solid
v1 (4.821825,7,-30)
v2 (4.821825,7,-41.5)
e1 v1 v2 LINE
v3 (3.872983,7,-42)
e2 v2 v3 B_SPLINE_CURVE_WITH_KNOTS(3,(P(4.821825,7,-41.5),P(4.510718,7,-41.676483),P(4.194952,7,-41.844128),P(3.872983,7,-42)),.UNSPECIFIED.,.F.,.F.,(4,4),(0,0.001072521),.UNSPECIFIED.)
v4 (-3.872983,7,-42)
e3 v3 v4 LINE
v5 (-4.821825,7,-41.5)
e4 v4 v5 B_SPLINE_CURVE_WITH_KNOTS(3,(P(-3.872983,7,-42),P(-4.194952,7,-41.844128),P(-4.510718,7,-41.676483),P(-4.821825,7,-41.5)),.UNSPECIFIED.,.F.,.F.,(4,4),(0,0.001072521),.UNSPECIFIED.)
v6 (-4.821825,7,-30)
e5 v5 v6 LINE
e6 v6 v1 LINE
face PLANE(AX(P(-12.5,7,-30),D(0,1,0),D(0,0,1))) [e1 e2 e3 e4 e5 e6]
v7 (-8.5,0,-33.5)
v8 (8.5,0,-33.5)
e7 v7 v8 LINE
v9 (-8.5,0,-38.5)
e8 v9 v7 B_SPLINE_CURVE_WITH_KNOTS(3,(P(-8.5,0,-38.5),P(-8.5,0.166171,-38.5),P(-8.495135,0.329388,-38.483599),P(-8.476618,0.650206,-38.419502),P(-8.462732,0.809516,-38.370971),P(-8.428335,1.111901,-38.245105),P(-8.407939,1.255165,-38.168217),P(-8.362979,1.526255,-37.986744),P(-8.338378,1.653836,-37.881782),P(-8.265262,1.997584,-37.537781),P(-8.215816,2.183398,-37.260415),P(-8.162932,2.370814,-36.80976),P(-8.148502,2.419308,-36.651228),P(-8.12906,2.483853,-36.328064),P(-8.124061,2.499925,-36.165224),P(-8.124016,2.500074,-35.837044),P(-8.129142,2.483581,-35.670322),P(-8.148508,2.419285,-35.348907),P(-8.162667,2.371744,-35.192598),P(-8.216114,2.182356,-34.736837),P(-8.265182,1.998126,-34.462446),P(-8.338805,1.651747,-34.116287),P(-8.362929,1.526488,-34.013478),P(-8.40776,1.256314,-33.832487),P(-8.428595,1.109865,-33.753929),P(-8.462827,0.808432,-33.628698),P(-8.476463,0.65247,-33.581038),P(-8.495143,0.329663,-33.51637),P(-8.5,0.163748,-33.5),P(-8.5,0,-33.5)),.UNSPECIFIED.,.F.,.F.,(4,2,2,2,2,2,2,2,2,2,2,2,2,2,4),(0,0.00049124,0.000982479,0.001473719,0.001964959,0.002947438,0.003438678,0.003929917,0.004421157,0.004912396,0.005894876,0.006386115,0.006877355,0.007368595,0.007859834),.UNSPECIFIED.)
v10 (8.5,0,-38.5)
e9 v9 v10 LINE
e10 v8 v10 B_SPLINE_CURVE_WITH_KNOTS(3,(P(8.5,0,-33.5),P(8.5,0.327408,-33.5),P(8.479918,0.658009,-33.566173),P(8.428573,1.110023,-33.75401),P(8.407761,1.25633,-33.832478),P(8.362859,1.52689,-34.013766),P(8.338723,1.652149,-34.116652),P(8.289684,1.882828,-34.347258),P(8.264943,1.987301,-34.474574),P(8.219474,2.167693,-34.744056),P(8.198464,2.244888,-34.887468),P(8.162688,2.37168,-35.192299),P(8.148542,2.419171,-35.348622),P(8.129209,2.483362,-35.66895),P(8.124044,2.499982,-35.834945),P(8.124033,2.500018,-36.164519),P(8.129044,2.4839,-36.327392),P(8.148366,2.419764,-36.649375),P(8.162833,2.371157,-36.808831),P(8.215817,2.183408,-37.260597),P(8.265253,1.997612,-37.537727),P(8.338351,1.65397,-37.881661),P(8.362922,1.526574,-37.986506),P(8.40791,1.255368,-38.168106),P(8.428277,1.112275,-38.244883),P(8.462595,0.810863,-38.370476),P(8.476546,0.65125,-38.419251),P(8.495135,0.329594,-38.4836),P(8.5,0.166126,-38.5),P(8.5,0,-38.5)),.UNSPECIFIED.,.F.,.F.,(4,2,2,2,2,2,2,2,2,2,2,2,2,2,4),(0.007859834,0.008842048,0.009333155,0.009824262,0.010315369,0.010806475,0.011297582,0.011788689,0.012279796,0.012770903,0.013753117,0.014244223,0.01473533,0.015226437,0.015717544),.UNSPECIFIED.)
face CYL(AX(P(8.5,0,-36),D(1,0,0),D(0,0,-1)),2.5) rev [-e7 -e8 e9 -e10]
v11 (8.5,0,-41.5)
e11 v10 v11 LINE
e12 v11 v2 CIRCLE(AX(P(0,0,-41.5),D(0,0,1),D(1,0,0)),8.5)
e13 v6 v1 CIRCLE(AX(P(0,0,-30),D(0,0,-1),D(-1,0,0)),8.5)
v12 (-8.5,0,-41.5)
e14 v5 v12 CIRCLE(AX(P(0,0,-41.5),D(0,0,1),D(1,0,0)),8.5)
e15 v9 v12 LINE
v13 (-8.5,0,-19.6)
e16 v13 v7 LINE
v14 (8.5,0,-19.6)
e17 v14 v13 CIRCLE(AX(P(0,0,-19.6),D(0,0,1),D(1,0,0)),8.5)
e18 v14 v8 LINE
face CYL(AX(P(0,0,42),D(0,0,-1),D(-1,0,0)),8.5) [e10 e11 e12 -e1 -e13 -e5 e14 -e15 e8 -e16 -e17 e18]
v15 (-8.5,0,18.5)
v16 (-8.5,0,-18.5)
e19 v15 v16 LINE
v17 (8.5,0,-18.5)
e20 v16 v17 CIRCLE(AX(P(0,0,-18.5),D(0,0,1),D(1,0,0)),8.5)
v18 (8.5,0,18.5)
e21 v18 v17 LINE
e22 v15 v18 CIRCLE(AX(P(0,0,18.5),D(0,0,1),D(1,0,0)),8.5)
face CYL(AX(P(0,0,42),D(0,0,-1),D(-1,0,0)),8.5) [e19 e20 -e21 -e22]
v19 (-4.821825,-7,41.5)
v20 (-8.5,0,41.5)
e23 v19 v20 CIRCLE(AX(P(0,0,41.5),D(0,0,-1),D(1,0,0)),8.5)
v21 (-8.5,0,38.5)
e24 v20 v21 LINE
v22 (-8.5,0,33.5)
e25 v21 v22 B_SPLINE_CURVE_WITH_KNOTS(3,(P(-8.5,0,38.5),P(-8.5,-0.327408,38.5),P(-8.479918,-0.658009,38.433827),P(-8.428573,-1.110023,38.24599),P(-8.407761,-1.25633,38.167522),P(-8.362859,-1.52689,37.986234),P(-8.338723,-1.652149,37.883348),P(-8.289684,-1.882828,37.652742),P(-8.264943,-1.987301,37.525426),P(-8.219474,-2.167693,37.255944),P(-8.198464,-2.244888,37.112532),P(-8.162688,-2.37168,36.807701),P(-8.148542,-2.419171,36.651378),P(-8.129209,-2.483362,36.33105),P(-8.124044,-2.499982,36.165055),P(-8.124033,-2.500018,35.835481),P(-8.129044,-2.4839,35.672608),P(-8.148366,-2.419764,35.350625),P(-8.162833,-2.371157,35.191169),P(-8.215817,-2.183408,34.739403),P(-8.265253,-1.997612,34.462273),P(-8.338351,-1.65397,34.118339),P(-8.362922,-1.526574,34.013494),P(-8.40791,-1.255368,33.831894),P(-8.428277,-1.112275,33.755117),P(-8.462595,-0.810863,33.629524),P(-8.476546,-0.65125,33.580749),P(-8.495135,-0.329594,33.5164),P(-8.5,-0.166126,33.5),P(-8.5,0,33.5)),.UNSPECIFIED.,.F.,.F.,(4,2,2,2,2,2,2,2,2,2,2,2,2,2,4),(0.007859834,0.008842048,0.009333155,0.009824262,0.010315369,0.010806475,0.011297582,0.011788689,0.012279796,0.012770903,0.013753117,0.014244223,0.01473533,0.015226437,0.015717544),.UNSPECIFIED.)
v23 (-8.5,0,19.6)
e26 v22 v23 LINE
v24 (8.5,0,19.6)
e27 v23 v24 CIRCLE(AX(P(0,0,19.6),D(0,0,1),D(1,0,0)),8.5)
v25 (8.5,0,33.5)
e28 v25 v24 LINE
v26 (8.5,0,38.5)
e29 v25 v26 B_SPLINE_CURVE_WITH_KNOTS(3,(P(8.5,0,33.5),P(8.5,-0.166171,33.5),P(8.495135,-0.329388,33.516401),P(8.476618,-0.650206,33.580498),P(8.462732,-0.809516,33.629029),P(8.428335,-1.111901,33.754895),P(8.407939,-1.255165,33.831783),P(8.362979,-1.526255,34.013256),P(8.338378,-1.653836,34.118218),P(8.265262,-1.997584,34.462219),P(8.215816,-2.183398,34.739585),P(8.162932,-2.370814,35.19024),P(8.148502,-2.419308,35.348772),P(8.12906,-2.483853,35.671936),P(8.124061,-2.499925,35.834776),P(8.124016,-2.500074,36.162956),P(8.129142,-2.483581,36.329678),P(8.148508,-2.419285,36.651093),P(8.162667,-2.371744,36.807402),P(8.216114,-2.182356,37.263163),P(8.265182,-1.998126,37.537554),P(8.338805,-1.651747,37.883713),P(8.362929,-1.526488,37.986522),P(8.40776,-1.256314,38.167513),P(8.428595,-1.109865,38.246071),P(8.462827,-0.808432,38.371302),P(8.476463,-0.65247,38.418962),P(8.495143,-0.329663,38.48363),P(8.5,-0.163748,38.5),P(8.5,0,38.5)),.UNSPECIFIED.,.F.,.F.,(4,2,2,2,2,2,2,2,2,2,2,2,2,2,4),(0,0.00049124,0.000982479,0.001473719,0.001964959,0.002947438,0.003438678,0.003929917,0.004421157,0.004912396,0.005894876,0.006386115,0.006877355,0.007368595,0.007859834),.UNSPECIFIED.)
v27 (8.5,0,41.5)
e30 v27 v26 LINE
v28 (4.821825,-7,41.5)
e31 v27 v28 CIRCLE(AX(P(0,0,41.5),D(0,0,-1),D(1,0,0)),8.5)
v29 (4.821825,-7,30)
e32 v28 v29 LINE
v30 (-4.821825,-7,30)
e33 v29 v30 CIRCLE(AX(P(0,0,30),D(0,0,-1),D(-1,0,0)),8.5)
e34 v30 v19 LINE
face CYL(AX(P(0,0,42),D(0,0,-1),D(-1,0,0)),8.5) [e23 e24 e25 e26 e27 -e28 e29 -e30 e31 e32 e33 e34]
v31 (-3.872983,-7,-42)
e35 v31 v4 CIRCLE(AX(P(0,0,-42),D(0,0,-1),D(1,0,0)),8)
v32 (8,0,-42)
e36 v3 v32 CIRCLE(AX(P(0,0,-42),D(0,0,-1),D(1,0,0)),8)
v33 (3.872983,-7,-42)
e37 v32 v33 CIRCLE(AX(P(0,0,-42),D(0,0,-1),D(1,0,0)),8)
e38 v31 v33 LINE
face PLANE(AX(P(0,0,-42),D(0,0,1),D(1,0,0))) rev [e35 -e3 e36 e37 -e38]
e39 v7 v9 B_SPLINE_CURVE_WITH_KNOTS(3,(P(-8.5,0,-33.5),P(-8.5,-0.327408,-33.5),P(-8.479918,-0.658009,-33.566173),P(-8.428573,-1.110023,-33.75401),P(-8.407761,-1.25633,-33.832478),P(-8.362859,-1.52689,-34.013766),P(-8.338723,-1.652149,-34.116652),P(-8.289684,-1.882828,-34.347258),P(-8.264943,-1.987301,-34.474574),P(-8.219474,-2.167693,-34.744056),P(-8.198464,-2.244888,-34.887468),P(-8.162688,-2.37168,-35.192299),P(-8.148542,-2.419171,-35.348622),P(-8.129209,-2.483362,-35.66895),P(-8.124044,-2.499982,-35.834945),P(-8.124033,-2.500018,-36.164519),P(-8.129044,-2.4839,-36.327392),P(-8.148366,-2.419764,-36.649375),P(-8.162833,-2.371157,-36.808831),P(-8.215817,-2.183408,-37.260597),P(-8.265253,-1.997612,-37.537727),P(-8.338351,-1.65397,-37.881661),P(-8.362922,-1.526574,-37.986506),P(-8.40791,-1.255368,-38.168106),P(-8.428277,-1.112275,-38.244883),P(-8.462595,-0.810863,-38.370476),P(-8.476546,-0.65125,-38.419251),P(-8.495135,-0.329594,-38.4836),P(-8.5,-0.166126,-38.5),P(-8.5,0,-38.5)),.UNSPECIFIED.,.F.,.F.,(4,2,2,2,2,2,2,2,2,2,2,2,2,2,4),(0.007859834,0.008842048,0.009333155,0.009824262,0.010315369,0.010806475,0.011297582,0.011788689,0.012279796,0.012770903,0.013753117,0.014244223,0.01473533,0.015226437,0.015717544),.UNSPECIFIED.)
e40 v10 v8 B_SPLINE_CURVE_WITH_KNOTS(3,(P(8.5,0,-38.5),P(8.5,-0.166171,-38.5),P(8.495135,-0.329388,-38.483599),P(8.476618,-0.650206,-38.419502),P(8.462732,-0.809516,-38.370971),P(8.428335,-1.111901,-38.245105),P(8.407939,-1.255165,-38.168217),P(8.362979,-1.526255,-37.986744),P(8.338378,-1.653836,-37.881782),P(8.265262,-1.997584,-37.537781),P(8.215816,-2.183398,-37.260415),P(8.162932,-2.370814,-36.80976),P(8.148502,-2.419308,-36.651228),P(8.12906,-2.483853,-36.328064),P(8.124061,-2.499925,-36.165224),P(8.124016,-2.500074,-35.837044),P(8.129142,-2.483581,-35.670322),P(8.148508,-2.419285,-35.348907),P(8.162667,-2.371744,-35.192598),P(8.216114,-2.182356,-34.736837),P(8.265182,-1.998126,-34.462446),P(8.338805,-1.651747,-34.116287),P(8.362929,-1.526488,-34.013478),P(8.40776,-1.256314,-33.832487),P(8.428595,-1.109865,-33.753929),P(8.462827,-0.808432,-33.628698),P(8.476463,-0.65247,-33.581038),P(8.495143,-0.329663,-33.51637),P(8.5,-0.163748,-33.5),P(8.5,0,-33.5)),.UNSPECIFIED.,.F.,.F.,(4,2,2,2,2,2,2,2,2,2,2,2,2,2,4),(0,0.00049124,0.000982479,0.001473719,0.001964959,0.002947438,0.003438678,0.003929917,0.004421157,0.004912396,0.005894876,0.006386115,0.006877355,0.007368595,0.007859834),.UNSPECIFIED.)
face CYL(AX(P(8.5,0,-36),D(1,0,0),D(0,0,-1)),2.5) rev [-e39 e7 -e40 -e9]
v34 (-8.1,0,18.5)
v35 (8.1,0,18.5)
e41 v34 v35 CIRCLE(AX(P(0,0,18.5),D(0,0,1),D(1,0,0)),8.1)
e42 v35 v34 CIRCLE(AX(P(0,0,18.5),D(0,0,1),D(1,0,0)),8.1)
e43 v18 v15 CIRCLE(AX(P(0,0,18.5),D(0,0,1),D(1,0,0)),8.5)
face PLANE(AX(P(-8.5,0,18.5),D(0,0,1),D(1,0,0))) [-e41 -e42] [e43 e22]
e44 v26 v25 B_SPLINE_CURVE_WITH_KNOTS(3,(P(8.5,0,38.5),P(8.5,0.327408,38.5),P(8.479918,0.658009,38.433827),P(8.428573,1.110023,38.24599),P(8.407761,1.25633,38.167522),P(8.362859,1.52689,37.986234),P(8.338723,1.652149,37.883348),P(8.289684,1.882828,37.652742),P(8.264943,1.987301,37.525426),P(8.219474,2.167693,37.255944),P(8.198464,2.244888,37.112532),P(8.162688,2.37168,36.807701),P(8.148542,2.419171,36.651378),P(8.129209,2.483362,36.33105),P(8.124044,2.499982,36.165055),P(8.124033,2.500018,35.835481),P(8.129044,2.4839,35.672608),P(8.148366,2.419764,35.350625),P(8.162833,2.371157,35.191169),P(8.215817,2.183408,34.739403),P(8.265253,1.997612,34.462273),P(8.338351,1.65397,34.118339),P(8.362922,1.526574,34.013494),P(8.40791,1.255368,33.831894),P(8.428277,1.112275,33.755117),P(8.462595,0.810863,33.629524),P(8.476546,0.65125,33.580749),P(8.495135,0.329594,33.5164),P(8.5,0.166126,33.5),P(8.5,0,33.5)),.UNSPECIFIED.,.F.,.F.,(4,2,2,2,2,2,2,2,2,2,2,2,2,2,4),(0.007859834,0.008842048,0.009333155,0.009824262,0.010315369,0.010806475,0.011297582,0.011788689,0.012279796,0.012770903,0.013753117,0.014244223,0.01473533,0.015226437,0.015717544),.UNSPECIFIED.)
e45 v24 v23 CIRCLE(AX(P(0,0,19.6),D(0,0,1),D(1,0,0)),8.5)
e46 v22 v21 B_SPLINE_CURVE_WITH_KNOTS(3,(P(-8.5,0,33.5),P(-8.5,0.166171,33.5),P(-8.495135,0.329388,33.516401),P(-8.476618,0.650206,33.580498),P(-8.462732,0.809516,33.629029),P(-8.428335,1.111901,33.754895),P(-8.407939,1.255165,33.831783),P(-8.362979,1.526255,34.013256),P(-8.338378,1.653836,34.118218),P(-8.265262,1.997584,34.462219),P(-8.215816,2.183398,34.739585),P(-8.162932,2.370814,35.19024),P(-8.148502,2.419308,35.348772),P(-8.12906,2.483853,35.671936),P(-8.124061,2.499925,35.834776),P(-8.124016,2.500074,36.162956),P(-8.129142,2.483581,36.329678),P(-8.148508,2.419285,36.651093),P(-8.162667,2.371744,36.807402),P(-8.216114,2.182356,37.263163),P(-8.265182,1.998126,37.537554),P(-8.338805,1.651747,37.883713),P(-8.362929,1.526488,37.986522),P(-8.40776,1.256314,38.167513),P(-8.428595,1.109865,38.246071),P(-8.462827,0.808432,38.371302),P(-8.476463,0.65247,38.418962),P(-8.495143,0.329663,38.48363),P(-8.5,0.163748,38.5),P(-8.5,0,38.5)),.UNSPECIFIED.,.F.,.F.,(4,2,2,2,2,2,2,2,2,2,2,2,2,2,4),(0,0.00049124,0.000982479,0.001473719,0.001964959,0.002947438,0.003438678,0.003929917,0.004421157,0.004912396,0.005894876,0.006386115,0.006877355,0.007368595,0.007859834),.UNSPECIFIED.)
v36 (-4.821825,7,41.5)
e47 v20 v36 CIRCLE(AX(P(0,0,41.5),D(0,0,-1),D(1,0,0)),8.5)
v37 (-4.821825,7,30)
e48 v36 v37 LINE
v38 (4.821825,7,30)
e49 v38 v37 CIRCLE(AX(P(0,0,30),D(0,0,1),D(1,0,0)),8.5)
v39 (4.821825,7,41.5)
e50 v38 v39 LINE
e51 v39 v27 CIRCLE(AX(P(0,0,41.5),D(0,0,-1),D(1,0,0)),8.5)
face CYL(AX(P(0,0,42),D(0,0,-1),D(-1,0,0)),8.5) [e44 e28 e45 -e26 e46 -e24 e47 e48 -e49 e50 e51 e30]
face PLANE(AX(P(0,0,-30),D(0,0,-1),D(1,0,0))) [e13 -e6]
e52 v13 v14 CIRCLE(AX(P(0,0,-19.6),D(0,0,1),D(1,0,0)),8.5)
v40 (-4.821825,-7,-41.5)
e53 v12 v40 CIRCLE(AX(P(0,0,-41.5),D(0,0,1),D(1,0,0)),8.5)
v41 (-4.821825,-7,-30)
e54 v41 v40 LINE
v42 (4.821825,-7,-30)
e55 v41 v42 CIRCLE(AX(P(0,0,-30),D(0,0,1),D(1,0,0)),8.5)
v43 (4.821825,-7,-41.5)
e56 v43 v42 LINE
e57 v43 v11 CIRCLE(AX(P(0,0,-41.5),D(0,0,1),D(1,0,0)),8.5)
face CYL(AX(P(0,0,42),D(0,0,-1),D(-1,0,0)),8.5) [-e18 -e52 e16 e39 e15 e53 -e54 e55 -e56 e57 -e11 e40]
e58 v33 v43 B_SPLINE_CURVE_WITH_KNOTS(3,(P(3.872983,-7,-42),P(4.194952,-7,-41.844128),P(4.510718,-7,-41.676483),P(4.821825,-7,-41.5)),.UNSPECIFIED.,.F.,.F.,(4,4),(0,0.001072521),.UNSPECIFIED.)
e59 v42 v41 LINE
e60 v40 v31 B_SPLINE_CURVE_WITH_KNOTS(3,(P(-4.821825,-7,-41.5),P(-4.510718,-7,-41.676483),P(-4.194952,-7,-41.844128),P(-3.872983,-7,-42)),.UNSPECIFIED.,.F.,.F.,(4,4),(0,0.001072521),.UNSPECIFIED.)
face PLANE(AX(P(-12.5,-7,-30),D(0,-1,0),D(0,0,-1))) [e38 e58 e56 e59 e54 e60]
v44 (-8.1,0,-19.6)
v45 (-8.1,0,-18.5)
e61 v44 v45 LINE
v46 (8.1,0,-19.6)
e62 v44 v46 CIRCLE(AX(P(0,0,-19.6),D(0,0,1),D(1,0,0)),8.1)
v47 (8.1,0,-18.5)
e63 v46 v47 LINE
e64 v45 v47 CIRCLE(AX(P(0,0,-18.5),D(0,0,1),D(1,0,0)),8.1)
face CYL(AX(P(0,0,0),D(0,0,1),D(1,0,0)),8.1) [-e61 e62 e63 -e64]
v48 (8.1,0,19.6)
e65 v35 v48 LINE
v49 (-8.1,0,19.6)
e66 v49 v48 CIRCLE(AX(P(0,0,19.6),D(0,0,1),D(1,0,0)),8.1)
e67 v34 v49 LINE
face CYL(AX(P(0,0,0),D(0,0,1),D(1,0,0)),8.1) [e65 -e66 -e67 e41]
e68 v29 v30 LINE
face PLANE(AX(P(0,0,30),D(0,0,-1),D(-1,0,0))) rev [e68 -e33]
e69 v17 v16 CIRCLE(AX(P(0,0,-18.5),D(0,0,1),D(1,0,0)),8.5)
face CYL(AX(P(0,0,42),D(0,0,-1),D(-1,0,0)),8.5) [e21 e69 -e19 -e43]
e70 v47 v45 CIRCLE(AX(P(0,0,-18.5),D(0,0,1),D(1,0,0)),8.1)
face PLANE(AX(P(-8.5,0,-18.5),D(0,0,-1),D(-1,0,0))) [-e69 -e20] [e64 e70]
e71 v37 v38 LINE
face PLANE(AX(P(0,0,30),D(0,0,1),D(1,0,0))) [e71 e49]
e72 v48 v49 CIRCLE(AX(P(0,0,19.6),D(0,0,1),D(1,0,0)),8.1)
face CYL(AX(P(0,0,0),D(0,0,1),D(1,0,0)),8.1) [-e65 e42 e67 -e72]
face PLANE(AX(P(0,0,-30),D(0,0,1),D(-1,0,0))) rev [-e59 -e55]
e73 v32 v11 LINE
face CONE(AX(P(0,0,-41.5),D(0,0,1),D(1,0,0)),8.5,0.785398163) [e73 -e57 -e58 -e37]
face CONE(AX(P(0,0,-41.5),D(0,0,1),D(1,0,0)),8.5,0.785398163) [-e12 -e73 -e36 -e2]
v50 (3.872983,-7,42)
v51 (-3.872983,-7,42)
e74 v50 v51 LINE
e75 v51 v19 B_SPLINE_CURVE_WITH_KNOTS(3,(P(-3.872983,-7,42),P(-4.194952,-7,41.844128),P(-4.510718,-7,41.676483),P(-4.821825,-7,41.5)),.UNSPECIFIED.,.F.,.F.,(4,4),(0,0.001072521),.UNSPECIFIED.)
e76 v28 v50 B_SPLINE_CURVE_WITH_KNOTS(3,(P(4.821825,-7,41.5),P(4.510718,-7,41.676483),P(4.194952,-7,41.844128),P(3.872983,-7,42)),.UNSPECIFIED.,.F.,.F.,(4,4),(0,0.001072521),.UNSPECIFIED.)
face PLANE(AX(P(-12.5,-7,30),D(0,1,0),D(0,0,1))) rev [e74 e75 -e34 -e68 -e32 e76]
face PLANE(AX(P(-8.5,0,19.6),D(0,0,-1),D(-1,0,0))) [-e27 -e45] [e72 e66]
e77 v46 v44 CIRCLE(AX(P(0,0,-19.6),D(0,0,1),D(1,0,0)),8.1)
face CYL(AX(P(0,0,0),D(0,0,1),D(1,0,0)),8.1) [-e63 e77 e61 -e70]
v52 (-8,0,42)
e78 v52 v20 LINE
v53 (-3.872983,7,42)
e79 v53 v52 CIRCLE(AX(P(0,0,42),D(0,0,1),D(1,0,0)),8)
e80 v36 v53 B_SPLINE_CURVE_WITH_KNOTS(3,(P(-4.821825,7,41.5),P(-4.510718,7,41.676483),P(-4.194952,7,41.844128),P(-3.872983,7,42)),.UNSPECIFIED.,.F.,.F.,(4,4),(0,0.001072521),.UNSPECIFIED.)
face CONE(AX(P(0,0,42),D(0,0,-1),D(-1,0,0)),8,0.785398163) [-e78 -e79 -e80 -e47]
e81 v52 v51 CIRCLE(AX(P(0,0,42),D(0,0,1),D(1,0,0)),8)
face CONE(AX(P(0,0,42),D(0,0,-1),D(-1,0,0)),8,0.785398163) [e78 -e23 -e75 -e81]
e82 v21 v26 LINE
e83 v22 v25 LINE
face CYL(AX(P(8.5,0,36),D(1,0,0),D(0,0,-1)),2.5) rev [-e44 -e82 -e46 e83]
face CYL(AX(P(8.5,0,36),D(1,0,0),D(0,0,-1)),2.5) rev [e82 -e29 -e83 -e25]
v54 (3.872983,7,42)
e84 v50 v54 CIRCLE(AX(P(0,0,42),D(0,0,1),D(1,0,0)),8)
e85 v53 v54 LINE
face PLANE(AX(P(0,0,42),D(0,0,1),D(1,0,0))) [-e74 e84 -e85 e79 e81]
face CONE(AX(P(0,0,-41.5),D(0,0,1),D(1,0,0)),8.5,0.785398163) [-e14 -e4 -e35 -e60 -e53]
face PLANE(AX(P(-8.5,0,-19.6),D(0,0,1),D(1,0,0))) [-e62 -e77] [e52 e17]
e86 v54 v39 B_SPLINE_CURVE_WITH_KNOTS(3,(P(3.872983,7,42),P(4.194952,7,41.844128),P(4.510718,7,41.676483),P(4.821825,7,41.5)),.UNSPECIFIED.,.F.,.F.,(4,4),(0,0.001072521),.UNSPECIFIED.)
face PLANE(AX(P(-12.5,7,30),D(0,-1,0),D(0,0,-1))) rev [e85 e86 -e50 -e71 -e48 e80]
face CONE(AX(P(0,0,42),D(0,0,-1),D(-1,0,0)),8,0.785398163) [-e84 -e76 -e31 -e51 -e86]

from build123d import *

# Parameters (mm, degrees)
SKETCH_1_R          = 8.5
EXTRUDE_1_DEPTH     = 42
SKETCH_2_W          = 25
SKETCH_2_H          = 3
CUT_EXTRUDE_1_DEPTH = 12
CHAMFER_2_SIZE      = 0.5
HOLE_WIZARD_M6_1_D  = 5
SKETCH_5_W          = 0.4
SKETCH_5_H          = 1.1


with BuildPart() as part:
    # 草图1 → 凸台-拉伸1 (new, symmetric)
    with BuildSketch(Plane.XY):
        with Locations(Location((0, 0, 0), (0, 0, 180))):
            Circle(SKETCH_1_R)
    extrude(amount=EXTRUDE_1_DEPTH, both=True)

    # 草图2 → 切除-拉伸1 (cut)
    with BuildSketch(Plane.XY.offset(42)):
        with Locations((0, 8.5)):
            Rectangle(SKETCH_2_W, SKETCH_2_H)
        with Locations((0, -8.5)):
            Rectangle(SKETCH_2_W, SKETCH_2_H)
    cut_extrude_1 = extrude(amount=-CUT_EXTRUDE_1_DEPTH, mode=Mode.SUBTRACT)

    # 镜向1: 切除-拉伸1 across plane
    add(cut_extrude_1.mirror(Plane.XY), mode=Mode.SUBTRACT)

    # 倒角2
    chamfer_2_edges = [part.edges().sort_by_distance(p)[0] for p in [
        (8.5, 0, 42),
        (-7.524477249, 3.953763034, -42),
        (8.5, 0, -42),
        (-7.524477249, 3.953763034, 42),
    ]]
    chamfer(chamfer_2_edges, length=CHAMFER_2_SIZE)

    # M6 螺纹孔1 (through all)
    with Locations(Plane(origin=(8.5, 0, 0), x_dir=(0, 0, -1), z_dir=(1, 0, 0))):
        with Locations((-36, 0), (36, 0)):
            Hole(HOLE_WIZARD_M6_1_D / 2)

    # 草图5 → 切除-旋转1 (revolve, cut)
    with BuildSketch(Plane(origin=(0, 0, 0), x_dir=(1, 0, 0), z_dir=(0, 1, 0)), mode=Mode.PRIVATE) as cut_revolve_1_sk:
        with Locations((-8.3, 19.05)):
            Rectangle(SKETCH_5_W, SKETCH_5_H)
        with Locations((-8.3, -19.05)):
            Rectangle(SKETCH_5_W, SKETCH_5_H)
    revolve(cut_revolve_1_sk.sketch.rotate(Axis((0, 0, 0), (0, 0, -1)), 180), axis=Axis((0, 0, 0), (0, 0, -1)), mode=Mode.SUBTRACT)


solid = part.part
